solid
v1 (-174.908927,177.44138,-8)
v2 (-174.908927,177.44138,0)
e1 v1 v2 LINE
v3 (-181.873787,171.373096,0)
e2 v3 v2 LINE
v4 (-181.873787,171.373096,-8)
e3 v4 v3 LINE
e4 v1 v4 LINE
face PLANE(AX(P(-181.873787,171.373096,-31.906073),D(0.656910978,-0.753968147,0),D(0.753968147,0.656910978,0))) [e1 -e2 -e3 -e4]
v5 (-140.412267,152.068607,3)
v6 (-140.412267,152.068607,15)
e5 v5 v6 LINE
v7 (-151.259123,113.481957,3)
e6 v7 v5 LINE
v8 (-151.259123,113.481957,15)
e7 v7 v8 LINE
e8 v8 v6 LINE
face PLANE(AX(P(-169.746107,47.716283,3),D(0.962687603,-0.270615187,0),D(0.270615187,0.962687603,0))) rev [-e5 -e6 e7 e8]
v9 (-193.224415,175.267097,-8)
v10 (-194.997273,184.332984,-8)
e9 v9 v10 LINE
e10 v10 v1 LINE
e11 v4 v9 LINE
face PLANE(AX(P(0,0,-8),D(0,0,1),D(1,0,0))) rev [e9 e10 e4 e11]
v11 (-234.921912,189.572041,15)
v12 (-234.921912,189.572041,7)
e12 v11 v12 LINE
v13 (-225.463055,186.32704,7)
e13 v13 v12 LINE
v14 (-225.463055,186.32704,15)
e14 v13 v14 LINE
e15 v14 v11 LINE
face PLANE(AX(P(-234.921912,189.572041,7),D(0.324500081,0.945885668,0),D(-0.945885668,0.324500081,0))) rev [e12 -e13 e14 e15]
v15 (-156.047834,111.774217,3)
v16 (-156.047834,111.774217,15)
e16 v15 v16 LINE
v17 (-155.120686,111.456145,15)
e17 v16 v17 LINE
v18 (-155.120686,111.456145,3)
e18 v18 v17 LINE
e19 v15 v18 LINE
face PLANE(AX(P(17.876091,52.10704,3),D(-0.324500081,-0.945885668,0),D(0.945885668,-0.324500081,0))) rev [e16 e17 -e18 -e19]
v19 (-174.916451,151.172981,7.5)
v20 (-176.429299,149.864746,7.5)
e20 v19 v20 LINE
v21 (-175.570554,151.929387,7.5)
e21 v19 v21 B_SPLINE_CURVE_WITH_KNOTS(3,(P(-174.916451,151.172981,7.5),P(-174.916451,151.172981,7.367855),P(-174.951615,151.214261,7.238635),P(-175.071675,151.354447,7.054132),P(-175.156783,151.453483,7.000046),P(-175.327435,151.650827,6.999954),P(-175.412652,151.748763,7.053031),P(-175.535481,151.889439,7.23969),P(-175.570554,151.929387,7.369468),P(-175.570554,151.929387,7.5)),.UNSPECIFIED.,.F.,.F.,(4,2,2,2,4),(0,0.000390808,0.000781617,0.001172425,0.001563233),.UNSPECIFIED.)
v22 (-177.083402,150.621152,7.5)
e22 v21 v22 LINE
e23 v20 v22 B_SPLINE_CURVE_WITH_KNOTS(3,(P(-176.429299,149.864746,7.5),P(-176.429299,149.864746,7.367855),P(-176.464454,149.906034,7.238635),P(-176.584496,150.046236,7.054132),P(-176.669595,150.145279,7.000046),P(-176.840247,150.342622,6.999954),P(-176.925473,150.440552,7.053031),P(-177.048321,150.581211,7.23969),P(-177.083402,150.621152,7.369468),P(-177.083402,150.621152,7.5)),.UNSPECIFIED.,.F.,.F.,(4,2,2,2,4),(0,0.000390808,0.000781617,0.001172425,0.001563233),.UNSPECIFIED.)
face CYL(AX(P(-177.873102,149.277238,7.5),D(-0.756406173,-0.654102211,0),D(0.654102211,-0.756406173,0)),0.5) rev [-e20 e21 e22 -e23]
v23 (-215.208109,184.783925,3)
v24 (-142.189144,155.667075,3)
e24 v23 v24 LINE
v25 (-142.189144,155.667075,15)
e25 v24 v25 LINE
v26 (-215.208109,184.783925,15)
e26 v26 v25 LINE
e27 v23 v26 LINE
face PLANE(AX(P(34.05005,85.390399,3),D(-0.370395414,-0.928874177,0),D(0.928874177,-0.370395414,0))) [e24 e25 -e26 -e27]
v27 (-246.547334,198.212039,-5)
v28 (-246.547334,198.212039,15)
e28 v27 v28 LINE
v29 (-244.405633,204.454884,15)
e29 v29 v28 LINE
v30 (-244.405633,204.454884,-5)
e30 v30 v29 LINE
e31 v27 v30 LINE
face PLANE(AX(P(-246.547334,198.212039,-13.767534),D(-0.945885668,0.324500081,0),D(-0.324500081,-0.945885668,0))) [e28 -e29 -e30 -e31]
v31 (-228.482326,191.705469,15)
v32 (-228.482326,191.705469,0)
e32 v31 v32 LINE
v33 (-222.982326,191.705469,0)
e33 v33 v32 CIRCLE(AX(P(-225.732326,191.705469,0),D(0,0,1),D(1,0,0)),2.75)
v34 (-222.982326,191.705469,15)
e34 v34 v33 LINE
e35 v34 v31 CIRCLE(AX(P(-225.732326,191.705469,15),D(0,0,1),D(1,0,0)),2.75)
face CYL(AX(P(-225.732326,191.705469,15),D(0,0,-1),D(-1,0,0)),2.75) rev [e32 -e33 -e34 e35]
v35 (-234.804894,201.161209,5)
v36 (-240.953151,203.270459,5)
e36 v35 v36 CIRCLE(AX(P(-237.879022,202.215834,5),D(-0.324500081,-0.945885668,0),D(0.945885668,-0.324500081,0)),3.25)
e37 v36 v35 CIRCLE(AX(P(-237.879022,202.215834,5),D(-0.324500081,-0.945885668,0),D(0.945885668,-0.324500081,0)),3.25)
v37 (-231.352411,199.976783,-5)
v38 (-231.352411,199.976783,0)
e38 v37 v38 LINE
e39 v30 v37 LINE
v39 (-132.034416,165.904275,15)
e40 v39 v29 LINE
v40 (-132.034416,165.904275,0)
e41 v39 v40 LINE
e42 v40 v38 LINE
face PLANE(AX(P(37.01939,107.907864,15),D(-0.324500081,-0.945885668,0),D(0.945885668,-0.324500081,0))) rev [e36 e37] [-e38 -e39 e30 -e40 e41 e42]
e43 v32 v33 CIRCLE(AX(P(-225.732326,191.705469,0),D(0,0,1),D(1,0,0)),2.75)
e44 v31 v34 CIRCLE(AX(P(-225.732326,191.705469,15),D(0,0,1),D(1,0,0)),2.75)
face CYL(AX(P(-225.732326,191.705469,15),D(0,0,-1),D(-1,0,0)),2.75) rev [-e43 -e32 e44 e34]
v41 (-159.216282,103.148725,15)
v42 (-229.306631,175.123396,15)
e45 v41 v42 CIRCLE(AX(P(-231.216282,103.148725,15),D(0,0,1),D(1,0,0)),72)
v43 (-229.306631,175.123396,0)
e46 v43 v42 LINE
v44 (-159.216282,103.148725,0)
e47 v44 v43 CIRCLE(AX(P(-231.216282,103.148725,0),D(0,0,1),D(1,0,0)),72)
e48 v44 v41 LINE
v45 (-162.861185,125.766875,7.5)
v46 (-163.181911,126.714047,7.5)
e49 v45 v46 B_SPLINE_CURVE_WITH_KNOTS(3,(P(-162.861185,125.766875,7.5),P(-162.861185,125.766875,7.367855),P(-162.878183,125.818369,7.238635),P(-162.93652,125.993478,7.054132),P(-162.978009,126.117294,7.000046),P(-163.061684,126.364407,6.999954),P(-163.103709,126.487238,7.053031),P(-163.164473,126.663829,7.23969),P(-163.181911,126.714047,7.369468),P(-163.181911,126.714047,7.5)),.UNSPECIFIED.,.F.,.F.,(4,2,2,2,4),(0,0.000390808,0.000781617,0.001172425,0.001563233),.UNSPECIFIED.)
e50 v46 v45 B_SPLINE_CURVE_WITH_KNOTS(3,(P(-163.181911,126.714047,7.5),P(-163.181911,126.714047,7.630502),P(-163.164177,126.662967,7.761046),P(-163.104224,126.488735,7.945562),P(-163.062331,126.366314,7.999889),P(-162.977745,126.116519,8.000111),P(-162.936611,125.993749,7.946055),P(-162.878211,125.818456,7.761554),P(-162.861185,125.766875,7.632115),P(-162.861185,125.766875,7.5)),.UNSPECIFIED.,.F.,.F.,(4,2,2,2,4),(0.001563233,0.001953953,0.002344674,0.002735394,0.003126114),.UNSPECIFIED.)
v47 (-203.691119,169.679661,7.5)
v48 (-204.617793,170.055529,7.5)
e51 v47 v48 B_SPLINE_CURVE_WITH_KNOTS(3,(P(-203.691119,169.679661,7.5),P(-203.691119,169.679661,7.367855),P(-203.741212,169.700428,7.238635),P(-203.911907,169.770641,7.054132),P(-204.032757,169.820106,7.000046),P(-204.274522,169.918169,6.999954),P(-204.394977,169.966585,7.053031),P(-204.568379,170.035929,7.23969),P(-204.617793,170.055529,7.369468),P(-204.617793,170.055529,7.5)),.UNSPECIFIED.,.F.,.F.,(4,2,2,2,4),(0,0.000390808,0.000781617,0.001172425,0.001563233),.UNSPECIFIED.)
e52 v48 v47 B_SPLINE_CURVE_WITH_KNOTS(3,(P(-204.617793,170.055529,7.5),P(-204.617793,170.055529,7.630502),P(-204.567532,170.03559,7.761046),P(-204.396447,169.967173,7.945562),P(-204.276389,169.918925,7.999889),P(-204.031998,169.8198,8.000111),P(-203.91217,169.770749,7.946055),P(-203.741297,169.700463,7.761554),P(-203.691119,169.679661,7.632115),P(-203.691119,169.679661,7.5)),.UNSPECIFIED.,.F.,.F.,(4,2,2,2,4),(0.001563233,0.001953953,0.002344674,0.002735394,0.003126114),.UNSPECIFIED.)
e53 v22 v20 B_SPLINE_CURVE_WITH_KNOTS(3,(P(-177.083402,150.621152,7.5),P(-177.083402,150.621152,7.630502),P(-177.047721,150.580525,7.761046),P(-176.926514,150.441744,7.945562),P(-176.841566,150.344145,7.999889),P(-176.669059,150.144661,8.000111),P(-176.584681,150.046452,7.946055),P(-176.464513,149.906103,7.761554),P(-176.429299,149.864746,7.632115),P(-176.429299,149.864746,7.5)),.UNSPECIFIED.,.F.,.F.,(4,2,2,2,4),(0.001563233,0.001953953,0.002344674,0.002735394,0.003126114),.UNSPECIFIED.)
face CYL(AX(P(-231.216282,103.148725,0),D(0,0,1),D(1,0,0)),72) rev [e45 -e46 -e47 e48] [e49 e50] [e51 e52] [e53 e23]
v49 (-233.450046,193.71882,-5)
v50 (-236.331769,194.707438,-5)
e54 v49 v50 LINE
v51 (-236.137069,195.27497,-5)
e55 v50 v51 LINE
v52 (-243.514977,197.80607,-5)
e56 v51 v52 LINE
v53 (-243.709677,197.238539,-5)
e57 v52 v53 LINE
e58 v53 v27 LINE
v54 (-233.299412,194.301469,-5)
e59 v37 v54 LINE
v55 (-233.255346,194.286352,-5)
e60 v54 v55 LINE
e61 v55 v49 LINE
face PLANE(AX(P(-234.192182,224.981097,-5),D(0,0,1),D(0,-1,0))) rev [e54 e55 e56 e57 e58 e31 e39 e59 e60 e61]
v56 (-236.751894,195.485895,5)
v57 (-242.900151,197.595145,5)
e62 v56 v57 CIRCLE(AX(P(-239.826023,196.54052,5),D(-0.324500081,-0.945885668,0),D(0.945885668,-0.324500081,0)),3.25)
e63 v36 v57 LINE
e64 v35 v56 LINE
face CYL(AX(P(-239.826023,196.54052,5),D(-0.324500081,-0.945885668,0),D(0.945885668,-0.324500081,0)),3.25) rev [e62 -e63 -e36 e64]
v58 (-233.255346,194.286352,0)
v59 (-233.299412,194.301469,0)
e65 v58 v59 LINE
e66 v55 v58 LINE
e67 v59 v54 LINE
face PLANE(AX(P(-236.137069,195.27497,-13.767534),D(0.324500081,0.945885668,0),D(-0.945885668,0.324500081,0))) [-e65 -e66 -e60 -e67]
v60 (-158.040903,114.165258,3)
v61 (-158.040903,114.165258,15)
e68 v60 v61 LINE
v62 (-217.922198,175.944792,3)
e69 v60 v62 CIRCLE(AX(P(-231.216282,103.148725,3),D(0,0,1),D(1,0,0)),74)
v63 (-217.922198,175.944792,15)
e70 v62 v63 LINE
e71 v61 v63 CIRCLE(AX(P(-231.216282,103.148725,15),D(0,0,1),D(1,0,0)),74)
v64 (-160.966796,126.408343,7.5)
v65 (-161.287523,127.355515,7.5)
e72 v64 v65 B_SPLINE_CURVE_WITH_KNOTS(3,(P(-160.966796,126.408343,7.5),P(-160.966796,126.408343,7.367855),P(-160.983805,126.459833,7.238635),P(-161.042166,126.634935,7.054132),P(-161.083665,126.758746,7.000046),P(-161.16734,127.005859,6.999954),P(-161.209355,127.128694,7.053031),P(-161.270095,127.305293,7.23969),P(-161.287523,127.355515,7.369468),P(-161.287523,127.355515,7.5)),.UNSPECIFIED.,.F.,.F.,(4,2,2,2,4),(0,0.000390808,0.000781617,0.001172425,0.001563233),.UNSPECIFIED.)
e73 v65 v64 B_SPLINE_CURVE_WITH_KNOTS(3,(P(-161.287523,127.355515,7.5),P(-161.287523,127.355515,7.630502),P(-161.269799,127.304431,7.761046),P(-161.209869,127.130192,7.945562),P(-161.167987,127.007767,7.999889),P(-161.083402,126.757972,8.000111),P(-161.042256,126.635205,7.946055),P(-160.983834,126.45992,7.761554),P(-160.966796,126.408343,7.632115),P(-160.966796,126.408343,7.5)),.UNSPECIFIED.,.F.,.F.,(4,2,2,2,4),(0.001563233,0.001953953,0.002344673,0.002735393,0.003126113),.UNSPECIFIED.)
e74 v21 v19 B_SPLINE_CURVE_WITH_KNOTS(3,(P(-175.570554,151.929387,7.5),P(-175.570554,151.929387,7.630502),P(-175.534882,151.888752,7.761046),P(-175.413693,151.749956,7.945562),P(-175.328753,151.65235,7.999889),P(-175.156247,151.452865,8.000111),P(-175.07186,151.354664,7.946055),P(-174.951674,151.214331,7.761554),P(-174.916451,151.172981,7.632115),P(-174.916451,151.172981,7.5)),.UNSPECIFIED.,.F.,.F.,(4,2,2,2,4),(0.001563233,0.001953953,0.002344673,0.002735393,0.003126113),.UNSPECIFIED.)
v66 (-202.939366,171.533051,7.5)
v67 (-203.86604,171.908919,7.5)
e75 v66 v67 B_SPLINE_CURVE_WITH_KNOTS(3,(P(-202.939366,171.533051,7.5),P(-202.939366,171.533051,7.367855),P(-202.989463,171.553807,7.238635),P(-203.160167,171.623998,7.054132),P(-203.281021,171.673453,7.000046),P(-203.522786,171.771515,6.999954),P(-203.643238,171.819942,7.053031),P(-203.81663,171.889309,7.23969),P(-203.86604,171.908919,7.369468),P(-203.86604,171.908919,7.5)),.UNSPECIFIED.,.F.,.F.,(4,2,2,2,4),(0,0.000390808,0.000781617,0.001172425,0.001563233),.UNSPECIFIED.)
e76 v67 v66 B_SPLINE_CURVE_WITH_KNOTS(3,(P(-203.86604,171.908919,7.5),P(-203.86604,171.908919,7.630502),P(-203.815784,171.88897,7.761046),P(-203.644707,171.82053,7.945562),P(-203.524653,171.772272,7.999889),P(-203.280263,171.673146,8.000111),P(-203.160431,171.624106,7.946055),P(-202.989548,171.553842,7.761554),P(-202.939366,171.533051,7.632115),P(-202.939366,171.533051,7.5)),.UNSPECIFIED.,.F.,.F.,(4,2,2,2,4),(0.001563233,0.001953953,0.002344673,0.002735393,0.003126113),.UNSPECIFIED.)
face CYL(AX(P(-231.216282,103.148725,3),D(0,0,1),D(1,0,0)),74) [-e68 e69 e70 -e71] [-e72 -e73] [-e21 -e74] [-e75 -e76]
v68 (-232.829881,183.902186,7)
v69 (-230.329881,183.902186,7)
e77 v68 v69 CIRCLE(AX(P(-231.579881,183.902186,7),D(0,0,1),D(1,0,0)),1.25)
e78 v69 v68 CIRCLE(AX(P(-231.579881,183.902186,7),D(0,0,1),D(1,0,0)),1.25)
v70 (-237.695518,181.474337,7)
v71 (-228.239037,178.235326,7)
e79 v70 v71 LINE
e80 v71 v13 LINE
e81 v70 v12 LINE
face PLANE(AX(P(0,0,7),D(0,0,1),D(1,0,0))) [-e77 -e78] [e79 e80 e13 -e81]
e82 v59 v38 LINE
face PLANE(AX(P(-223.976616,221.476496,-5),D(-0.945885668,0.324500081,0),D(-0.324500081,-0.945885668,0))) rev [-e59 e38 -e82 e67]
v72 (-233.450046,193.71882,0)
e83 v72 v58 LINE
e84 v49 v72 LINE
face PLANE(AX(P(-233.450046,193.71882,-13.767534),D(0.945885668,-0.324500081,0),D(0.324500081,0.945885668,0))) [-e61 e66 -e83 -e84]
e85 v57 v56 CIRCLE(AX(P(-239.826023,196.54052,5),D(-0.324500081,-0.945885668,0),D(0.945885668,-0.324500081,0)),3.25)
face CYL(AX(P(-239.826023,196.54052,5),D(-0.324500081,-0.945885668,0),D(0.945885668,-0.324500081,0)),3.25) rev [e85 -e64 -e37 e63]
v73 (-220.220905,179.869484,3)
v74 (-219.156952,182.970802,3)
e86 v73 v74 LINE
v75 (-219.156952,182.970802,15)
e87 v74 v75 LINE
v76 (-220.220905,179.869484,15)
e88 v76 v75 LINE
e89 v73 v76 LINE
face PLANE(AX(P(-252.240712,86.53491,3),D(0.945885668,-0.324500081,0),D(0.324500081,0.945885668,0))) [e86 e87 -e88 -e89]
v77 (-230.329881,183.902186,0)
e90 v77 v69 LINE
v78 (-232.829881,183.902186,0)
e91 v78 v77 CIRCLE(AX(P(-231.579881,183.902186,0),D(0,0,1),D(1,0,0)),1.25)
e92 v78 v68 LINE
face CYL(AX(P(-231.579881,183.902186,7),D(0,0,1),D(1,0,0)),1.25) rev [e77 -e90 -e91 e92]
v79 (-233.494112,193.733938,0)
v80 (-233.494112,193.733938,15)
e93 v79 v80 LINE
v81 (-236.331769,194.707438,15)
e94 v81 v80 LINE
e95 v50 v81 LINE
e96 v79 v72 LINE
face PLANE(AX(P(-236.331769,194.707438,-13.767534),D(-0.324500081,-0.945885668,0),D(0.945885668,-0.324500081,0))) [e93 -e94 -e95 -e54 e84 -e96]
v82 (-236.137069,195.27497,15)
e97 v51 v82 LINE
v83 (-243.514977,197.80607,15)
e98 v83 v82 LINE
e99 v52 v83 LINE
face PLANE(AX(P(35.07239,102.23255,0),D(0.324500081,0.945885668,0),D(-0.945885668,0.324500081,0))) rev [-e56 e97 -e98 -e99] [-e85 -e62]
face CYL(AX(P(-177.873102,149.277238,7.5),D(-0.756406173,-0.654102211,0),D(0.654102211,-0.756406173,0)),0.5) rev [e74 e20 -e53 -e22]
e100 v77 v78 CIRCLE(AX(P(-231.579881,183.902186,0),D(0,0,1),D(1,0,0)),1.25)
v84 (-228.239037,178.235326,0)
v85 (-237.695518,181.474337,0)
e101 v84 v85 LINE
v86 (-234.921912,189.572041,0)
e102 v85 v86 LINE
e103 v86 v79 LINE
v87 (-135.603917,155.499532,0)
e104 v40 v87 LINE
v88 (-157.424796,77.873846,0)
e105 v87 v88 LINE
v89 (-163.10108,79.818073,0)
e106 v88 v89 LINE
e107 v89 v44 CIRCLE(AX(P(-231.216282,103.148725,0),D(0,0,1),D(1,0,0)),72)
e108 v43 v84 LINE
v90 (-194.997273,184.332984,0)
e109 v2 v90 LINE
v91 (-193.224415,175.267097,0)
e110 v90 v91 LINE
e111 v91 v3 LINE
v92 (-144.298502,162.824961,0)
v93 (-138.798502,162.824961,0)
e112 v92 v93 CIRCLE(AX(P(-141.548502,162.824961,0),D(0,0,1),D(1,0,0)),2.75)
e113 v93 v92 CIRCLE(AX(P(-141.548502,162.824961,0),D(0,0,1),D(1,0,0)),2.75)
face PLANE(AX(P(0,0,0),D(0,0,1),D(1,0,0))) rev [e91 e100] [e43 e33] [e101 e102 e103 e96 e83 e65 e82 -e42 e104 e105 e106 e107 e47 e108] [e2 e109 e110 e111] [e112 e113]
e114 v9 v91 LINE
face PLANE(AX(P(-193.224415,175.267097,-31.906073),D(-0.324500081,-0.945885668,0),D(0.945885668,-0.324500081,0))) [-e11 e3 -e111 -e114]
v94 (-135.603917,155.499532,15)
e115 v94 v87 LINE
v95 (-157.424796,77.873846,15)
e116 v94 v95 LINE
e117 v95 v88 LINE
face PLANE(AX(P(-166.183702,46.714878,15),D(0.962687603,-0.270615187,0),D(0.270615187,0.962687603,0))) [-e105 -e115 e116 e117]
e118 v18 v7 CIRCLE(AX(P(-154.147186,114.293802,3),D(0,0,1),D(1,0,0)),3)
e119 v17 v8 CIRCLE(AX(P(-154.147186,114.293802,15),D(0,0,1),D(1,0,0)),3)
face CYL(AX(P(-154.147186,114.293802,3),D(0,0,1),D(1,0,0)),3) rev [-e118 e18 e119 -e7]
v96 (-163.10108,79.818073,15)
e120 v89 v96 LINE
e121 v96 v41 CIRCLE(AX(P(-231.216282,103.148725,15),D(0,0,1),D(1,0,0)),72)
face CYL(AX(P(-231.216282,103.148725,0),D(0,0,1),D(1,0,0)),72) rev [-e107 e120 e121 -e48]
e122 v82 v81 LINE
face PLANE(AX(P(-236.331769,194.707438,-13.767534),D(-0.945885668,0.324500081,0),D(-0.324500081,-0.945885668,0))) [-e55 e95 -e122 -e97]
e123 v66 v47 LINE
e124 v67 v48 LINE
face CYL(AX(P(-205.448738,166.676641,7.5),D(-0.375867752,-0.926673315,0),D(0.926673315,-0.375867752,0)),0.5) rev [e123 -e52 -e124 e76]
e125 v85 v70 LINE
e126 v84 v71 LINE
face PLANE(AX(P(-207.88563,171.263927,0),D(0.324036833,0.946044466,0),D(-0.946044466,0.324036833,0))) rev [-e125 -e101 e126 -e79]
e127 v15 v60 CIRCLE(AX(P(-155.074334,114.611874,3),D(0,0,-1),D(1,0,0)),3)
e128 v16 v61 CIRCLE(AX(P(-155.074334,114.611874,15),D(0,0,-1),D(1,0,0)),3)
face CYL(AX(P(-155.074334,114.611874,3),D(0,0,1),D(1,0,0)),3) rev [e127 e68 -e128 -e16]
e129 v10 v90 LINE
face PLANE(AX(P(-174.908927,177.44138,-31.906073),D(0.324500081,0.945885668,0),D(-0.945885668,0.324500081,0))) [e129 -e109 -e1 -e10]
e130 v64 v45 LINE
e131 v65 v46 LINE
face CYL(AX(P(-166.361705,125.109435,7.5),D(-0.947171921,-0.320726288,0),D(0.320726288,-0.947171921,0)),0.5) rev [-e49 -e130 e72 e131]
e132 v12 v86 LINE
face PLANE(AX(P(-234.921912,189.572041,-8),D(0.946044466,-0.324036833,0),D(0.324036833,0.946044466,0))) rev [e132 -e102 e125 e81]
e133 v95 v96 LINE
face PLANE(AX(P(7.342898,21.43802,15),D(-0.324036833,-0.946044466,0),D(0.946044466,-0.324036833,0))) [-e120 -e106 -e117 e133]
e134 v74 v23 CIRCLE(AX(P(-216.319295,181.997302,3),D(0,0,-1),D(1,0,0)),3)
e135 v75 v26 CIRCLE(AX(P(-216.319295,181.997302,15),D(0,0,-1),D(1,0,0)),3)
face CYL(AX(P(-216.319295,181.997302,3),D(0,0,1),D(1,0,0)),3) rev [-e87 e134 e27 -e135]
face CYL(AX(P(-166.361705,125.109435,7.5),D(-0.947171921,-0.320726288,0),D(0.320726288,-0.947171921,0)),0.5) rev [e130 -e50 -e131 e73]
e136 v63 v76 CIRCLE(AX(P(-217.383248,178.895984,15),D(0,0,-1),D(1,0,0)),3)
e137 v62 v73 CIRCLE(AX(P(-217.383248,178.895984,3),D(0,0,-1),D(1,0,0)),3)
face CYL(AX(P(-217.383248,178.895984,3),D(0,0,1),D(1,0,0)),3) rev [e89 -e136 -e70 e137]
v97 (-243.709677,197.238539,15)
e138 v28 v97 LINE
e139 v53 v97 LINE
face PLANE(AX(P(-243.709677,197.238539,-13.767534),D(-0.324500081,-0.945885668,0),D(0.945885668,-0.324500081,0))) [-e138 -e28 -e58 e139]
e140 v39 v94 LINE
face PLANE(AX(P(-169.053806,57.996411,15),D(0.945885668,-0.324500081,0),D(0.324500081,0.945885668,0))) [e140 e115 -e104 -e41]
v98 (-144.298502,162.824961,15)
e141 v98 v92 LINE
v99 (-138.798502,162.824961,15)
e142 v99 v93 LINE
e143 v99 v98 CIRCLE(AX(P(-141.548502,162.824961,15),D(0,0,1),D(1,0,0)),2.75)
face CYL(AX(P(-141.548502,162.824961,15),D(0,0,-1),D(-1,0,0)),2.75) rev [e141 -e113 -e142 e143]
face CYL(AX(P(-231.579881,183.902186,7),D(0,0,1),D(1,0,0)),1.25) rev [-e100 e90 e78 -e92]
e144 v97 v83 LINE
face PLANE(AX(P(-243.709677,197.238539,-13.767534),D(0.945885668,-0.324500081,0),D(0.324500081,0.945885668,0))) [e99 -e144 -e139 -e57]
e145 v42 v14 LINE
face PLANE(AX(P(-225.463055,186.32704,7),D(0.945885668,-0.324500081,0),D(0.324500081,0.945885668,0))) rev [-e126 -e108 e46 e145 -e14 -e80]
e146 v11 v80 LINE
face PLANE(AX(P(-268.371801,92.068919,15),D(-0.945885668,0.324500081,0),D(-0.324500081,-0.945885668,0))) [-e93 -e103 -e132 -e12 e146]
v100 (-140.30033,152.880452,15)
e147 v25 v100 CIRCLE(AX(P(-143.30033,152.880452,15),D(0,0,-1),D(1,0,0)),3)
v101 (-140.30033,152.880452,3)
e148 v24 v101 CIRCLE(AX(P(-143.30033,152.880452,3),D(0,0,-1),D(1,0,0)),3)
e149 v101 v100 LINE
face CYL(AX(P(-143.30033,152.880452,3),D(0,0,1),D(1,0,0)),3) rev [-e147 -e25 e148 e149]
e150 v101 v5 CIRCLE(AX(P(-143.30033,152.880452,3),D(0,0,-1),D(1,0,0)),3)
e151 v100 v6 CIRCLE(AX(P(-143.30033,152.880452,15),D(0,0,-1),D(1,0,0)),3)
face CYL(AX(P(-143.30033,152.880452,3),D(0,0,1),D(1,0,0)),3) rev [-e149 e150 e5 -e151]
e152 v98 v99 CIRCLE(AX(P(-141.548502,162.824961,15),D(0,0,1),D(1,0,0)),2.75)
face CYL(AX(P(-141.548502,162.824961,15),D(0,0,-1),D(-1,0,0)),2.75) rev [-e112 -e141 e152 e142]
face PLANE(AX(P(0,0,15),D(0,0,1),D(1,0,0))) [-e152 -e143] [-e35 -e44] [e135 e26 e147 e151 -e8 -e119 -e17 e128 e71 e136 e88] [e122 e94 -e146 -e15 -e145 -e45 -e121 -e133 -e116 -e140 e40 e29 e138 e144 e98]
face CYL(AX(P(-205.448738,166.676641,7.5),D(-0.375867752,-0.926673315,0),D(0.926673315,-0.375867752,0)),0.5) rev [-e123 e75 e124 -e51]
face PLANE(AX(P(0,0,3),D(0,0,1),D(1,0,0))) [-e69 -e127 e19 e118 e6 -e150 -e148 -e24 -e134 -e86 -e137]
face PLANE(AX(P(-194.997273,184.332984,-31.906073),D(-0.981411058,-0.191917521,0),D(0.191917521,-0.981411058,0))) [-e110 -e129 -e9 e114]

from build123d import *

# Parameters (mm, degrees)
EXTRUDE_1_DEPTH     = 8
SKETCH_2_R          = 2.75
EXTRUDE_2_DEPTH     = 15
CUT_EXTRUDE_1_DEPTH = 15
CUT_EXTRUDE_2_DEPTH = 8
CUT_EXTRUDE_3_DEPTH = 317.803371085
SKETCH_7_R          = 0.5
CUT_EXTRUDE_4_DEPTH = 311.990149374
EXTRUDE_3_DEPTH     = 15
SKETCH_9_W          = 10.8
SKETCH_9_H          = 20
EXTRUDE_4_DEPTH     = 6
EXTRUDE_5_REACH     = 320.172
SKETCH_12_W         = 3.25
SKETCH_12_H         = 42.464469098
EXTRUDE_6_DEPTH     = 15
CUT_EXTRUDE_5_DEPTH = 12
HOLE_WIZARD_M3_1_D  = 2.5


with BuildPart() as part:
    # 草图1 → 凸台-拉伸1 (new body)
    with BuildSketch(Plane.XY):
        Polygon((-181.873786677, 171.373096295), (-174.908927271, 177.441379972), (-194.997272817, 184.33298428), (-193.224414699, 175.267097261), align=None)
    extrude(amount=-EXTRUDE_1_DEPTH)



with BuildPart() as body_2:
    # 草图2 → 凸台-拉伸2 (new body)
    with BuildSketch(Plane.XY):
        with BuildLine():
            Line((-234.92191194, 189.572040939), (-267.921572877, 171.97259121))
            ThreePointArc((-267.921572877, 171.97259121), (-290.600732502, 153.720356817), (-305.007767585, 128.423604423))
            Line((-305.007767585, 128.423604423), (-293.655216332, 124.535156375))
            ThreePointArc((-293.655216332, 124.535156375), (-209.829850624, 165.587660123), (-168.777346876, 81.762294415))
            Line((-168.777346876, 81.762294415), (-157.424795623, 77.873846368))
            Line((-157.424795623, 77.873846368), (-135.603916755, 155.499532484))
            Line((-135.603916755, 155.499532484), (-132.034415869, 165.904274837))
            Line((-132.034415869, 165.904274837), (-231.352411054, 199.976783292))
            Line((-231.352411054, 199.976783292), (-234.92191194, 189.572040939))
        make_face()
        with Locations((-141.5485017, 162.824961471)):
            Circle(SKETCH_2_R, mode=Mode.SUBTRACT)
        with Locations((-225.73232619, 191.705468637)):
            Circle(SKETCH_2_R, mode=Mode.SUBTRACT)
        Polygon((-193.224414699, 175.267097261), (-181.873786677, 171.373096295), (-174.908927271, 177.441379972), (-194.997272817, 184.33298428), align=None, mode=Mode.SUBTRACT)
    extrude(amount=EXTRUDE_2_DEPTH)

    # 草图4 → 切除-拉伸1 (cut)
    with BuildSketch(Plane.XY.offset(15)):
        with BuildLine():
            Line((-207.885629626, 171.263926916), (-296.983281013, 201.781436227))
            Line((-296.983281013, 201.781436227), (-325.469194549, 118.615147397))
            Line((-325.469194549, 118.615147397), (-168.25634164, 64.766986109))
            Line((-168.25634164, 64.766986109), (-163.101080083, 79.818073417))
            ThreePointArc((-163.101080083, 79.818073417), (-166.554298483, 134.81618407), (-207.885629626, 171.263926916))
        make_face()
    extrude(amount=-CUT_EXTRUDE_1_DEPTH, mode=Mode.SUBTRACT)

    # 草图5 → 切除-拉伸2 (cut)
    with BuildSketch(Plane.XY.offset(15)):
        Polygon((-234.92191194, 189.572040939), (-225.463055256, 186.327040134), (-228.266951451, 178.153959799), (-237.725808135, 181.398960604), (-253.997826946, 186.981317532), (-251.193930751, 195.154397867), align=None)
    extrude(amount=-CUT_EXTRUDE_2_DEPTH, mode=Mode.SUBTRACT)

    # 草图6 → 切除-拉伸3 (cut, through all)
    with BuildSketch(Plane.XY.offset(7)):
        Polygon((-234.92191194, 189.572040939), (-237.695517736, 181.474336773), (-249.379698977, 185.476373912), (-246.606093182, 193.574078078), align=None)
    extrude(amount=-CUT_EXTRUDE_3_DEPTH, mode=Mode.SUBTRACT)

    # 草图7 → 切除-拉伸4 (cut, through all)
    with BuildSketch(Plane.XY.offset(7)):
        with Locations((-231.579880599, 183.90218604)):
            Circle(SKETCH_7_R)
    extrude(amount=-CUT_EXTRUDE_4_DEPTH, mode=Mode.SUBTRACT)

    # 草图8 → 凸台-拉伸3 (add)
    with BuildSketch(Plane.XY.offset(15)):
        with BuildLine():
            Line((-229.30663116, 175.123396184), (-228.239037464, 178.235326314))
            Line((-228.239037464, 178.235326314), (-207.885629626, 171.263926916))
            ThreePointArc((-207.885629626, 171.263926916), (-218.449445961, 174.007796146), (-229.30663116, 175.123396184))
        make_face()
    extrude(amount=-EXTRUDE_3_DEPTH)

    # 草图9 → 凸台-拉伸4 (add)
    with BuildSketch(Plane(origin=(35.072389683, 102.232550158, 0), x_dir=(0.9458856684293919, -0.324500080523692, 0), z_dir=(0.32450008052369195, 0.9458856684293918, 0))):
        with Locations((-289.125412254, -5)):
            Rectangle(SKETCH_9_W, SKETCH_9_H)
    extrude(amount=EXTRUDE_4_DEPTH)

    # 凸台-拉伸5: up to this face of the body (flat: up to its plane)
    extrude_5_end = Plane(body_2.part.faces().sort_by_distance((-237.433693905, 198.891426721, -5))[0])
    # 草图10 → 凸台-拉伸5 (add, up to the picked face)
    with BuildSketch(Plane.XY.offset(15), mode=Mode.PRIVATE) as extrude_5_sk1:
        Polygon((-236.331768591, 194.707438122), (-236.137068543, 195.274969523), (-233.255345678, 194.286351836), (-233.450045726, 193.718820435), align=None)
    extrude_5_tool1 = split(extrude(extrude_5_sk1.sketch, amount=-EXTRUDE_5_REACH, mode=Mode.PRIVATE), bisect_by=extrude_5_end, keep=Keep.BOTH, mode=Mode.PRIVATE)
    # 草图10 → 凸台-拉伸5 (add, up to the picked face)
    with BuildSketch(Plane.XY.offset(15), mode=Mode.PRIVATE) as extrude_5_sk2:
        Polygon((-243.709676805, 197.23853875), (-246.54733381, 198.212038991), (-244.405633279, 204.454884403), (-241.567976273, 203.481384162), align=None)
    extrude_5_tool2 = split(extrude(extrude_5_sk2.sketch, amount=-EXTRUDE_5_REACH, mode=Mode.PRIVATE), bisect_by=extrude_5_end, keep=Keep.BOTH, mode=Mode.PRIVATE)
    add(extrude_5_tool1.solids().sort_by(Axis((-234.793557, 194.496895, 15), (0, 0, -1)))[0])
    add(extrude_5_tool2.solids().sort_by(Axis((-244.057655, 200.846712, 15), (0, 0, -1)))[0])

    # 草图12 → Ø1.0 (1) 直径孔1 (revolve, cut)
    with BuildSketch(Plane(origin=(-239.82602265, 196.540519837, 5), x_dir=(0.9458856684293919, -0.32450008052369167, 0), z_dir=(0, 0, 1))):
        with Locations((1.625, 21.232234549)):
            Rectangle(SKETCH_12_W, SKETCH_12_H)
    revolve(axis=Axis((-241.886598161, 190.534145842, 5), (0.3245000805236916, 0.945885668429392, 0)), mode=Mode.SUBTRACT)


with BuildPart() as part_1:
    add(part.part)

    add(body_2.part)  # 凸台-拉伸6 merges body 2
    # 草图13 → 凸台-拉伸6 (add)
    with BuildSketch(Plane.XY):
        Polygon((-193.224414699, 175.267097261), (-181.873786677, 171.373096295), (-174.908927271, 177.441379972), (-194.997272817, 184.33298428), align=None)
    extrude(amount=EXTRUDE_6_DEPTH)

    # 草图14 → 切除-拉伸5 (cut)
    with BuildSketch(Plane.XY.offset(15)):
        with BuildLine():
            ThreePointArc((-156.047834036, 111.774217336), (-157.378743964, 112.691016779), (-158.04090319, 114.165258148))
            ThreePointArc((-158.04090319, 114.165258148), (-178.080420962, 154.651932226), (-217.922197627, 175.944792124))
            ThreePointArc((-217.922197627, 175.944792124), (-219.971910037, 177.379794621), (-220.220905282, 179.86948426))
            Line((-220.220905282, 179.86948426), (-219.156952171, 182.97080244))
            ThreePointArc((-219.156952171, 182.97080244), (-217.571105228, 184.723649859), (-215.208108923, 184.78392473))
            Line((-215.208108923, 184.78392473), (-142.189143758, 155.667074982))
            ThreePointArc((-142.189143758, 155.667074982), (-140.610396656, 154.208706418), (-140.412267192, 152.068606889))
            Line((-140.412267192, 152.068606889), (-151.259122885, 113.481956899))
            ThreePointArc((-151.259122885, 113.481956899), (-152.753497975, 111.637181572), (-155.120685935, 111.456145455))
            Line((-155.120685935, 111.456145455), (-156.047834036, 111.774217336))
        make_face()
    extrude(amount=-CUT_EXTRUDE_5_DEPTH, mode=Mode.SUBTRACT)

    # 草图15 → 切除-旋转1 (revolve, cut)
    with BuildSketch(Plane.XY.offset(7.5)):
        Polygon((-205.4487383, 166.676640825), (-201.772468541, 175.740203913), (-201.309131883, 175.552270037), (-204.985401642, 166.488706949), align=None)
    revolve(axis=Axis((-205.4487383, 166.676640825, 7.5), (0.375867752200837, 0.9266733150660432, 0)), mode=Mode.SUBTRACT)

    # 草图16 → 切除-旋转2 (revolve, cut)
    with BuildSketch(Plane.XY.offset(7.5)):
        Polygon((-177.87310191, 149.277238135), (-169.262777578, 156.723015795), (-168.935726472, 156.344812709), (-177.546050805, 148.899035049), align=None)
    revolve(axis=Axis((-177.87310191, 149.277238135, 7.5), (0.75640617255012, 0.6541022107653192, 0)), mode=Mode.SUBTRACT)

    # 草图17 → 切除-旋转3 (revolve, cut)
    with BuildSketch(Plane.XY.offset(7.5)):
        Polygon((-166.361705167, 125.109435071), (-154.938042437, 128.977654623), (-154.777679293, 128.504068663), (-166.201342023, 124.63584911), align=None)
    revolve(axis=Axis((-166.361705167, 125.109435071, 7.5), (0.9471719210759217, 0.3207262881731836, 0)), mode=Mode.SUBTRACT)

    # M3 螺纹孔1 (through all)
    with Locations(Plane.XY.offset(7)):
        with Locations((-231.579880599, 183.90218604)):
            Hole(HOLE_WIZARD_M3_1_D / 2)


solid = part_1.part
